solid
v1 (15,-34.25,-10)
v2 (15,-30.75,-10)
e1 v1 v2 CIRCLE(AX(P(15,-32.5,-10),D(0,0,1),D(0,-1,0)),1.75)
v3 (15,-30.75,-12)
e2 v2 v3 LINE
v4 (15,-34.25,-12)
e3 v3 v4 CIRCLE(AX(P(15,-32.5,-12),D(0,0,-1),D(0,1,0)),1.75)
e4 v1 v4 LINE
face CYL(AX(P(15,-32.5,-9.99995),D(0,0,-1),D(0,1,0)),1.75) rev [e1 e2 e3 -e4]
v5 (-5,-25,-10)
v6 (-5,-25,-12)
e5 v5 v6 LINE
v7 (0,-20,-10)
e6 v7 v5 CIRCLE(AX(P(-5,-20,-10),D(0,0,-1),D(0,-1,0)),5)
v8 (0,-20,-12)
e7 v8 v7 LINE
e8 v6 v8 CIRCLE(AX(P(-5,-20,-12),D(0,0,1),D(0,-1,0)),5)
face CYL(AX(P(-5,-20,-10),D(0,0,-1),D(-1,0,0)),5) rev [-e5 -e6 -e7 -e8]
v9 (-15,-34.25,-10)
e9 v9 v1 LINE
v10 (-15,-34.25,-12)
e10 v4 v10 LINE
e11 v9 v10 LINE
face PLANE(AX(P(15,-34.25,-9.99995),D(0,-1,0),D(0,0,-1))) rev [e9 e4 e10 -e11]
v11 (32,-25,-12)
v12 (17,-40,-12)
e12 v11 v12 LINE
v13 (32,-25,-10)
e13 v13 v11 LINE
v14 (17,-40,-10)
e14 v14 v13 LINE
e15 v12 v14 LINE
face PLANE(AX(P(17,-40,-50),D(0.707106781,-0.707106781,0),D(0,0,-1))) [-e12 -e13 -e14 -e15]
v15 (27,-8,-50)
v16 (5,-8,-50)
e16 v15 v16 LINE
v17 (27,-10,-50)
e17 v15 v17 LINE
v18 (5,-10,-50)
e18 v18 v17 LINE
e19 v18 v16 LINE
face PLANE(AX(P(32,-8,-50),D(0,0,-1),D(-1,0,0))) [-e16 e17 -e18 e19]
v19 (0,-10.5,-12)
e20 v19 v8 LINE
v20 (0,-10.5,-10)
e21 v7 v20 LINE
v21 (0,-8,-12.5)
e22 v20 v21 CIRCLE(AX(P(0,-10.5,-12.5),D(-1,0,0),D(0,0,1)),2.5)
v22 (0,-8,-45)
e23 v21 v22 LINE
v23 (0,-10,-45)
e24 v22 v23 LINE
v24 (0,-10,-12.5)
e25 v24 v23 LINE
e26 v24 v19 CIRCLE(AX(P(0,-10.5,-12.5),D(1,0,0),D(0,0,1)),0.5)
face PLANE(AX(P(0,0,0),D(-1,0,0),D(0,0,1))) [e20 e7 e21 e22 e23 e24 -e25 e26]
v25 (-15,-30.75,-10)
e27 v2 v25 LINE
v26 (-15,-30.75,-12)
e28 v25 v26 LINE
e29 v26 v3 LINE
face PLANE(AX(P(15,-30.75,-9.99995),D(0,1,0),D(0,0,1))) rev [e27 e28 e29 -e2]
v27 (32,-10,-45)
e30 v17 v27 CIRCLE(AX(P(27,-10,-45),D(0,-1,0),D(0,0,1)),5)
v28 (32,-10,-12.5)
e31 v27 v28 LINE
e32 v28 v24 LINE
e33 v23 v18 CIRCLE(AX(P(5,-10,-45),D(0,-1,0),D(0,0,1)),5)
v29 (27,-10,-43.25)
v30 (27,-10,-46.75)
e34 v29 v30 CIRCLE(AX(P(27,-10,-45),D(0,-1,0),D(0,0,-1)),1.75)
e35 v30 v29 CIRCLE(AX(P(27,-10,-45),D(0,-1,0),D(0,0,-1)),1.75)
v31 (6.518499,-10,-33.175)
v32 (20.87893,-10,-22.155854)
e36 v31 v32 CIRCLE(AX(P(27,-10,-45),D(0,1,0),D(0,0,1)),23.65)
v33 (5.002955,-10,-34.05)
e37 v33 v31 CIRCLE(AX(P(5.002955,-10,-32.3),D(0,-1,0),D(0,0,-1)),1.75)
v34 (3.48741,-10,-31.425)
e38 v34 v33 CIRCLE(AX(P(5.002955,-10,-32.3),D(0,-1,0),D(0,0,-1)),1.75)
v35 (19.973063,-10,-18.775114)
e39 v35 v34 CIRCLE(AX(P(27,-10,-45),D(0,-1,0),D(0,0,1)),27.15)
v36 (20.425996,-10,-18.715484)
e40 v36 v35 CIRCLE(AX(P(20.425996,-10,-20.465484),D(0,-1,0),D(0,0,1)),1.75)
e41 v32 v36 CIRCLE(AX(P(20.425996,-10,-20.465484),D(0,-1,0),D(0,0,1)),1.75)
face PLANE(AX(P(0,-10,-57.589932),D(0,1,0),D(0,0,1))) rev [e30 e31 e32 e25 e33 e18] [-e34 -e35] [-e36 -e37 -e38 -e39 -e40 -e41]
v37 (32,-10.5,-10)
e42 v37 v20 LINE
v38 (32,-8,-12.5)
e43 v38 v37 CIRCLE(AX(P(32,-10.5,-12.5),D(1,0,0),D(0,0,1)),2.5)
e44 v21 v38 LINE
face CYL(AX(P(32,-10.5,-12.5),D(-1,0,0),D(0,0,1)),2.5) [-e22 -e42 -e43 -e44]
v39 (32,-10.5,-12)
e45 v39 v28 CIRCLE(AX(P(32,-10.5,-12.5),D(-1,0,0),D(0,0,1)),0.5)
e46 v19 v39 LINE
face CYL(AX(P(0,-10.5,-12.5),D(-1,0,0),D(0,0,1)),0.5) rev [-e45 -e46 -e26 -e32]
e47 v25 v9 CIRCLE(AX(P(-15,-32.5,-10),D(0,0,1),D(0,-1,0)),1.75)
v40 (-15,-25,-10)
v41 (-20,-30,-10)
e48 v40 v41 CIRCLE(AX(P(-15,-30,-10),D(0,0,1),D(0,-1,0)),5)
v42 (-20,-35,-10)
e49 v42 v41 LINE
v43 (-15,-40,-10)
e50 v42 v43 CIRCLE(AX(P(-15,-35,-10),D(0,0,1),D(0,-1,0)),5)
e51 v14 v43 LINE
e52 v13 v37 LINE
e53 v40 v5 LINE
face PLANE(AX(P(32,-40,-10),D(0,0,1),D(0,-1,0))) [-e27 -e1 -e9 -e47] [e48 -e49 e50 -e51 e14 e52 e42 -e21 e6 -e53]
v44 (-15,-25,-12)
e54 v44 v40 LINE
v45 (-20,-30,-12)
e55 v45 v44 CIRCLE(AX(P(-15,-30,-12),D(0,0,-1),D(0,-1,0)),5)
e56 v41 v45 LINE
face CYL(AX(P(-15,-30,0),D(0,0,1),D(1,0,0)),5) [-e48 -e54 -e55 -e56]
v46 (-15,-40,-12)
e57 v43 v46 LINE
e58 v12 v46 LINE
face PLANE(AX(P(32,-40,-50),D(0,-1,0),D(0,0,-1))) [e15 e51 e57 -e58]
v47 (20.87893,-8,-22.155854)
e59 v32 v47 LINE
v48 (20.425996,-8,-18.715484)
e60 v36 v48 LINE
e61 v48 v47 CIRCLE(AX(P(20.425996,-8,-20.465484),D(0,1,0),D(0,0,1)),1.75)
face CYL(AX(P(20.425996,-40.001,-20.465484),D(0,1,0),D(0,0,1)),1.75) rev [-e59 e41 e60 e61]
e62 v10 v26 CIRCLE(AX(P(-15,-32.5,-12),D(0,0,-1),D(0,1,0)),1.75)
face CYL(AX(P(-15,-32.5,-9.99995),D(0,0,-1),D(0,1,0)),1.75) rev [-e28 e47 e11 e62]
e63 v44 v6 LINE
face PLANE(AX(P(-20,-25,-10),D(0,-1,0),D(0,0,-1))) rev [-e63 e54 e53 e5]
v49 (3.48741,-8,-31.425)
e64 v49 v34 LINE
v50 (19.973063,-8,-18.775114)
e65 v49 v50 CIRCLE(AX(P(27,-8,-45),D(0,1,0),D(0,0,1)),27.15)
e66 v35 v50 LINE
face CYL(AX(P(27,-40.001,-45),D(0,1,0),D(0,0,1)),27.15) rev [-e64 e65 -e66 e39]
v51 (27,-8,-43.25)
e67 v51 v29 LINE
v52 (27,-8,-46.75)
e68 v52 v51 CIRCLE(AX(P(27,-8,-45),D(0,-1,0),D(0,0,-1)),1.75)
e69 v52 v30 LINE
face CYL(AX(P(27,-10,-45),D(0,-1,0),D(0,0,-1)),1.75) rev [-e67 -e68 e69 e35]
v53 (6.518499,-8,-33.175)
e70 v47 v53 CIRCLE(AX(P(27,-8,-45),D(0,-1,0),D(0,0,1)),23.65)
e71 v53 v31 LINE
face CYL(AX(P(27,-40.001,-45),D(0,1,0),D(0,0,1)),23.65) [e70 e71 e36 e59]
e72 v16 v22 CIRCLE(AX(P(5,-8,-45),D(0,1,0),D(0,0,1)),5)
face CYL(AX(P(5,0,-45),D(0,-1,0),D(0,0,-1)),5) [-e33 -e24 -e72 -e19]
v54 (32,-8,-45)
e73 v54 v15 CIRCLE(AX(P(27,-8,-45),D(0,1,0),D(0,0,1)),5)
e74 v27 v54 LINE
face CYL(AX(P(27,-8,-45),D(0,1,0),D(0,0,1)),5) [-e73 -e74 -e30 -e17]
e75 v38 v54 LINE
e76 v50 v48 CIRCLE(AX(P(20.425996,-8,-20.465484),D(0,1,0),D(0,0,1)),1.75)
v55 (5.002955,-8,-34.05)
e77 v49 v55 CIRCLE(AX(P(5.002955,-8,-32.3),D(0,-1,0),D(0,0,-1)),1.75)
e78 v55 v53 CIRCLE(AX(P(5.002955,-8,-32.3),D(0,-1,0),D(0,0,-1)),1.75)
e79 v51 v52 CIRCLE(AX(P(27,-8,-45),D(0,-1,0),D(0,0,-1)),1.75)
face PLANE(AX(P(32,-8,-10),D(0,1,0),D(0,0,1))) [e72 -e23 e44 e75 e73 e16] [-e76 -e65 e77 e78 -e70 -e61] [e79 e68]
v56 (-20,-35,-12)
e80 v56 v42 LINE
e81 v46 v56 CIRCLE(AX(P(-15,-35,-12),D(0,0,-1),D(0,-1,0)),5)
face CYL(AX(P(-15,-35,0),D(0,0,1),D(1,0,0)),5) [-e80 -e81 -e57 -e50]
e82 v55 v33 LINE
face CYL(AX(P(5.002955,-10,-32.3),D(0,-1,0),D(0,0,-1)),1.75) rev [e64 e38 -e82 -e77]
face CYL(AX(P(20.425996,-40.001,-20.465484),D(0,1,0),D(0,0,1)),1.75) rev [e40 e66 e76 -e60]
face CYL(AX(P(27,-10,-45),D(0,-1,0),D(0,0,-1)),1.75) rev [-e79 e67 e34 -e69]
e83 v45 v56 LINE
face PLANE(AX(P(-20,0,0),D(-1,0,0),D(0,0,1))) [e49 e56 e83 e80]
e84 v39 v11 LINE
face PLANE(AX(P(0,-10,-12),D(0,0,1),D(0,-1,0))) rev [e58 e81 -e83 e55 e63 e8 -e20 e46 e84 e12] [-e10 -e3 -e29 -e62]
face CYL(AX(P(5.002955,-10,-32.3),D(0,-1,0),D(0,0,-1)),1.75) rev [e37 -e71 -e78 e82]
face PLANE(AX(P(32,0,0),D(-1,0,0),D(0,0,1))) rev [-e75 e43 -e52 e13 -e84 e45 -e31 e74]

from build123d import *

# Parameters (mm, degrees)
SKETCH_1_W              = 32
SKETCH_1_H              = 40
EXTRUDE_1_DEPTH         = 32
SKETCH_2_W              = 45.589932218
SKETCH_2_H              = 35.821991612
CUT_EXTRUDE_1_DEPTH     = 72.582120673
HOLE_WIZARD_3_5_3_5_1_D = 3.5
FILLET_1_R              = 0.5
FILLET_3_R              = 2.5
CUT_EXTRUDE_3_REACH     = 69.439
SKETCH_9_W              = 2
SKETCH_9_H              = 15
EXTRUDE_2_DEPTH         = 20
CUT_EXTRUDE_4_DEPTH     = 64.780874876
CHAMFER_1_SIZE          = 15
FILLET_4_R              = 5


with BuildPart() as part:
    # 草图1 → 凸台-拉伸1 (new body)
    with BuildSketch(Plane(origin=(0, 0, 0), x_dir=(0, -1, 0), z_dir=(-1, 0, 0))):
        with Locations((24, -30)):
            Rectangle(SKETCH_1_W, SKETCH_1_H)
    extrude(amount=-EXTRUDE_1_DEPTH)

    # 草图2 → 切除-拉伸1 (cut, through all)
    with BuildSketch(Plane(origin=(32, 0, 0), x_dir=(0, 0, -1), z_dir=(1, 0, 0))):
        with Locations((34.794966109, -27.910995806)):
            Rectangle(SKETCH_2_W, SKETCH_2_H)
    extrude(amount=-CUT_EXTRUDE_1_DEPTH, mode=Mode.SUBTRACT)

    # Ø3.5 (3.5) 直径孔1 (through all)
    with Locations(Plane(origin=(0, -10, 0), x_dir=(-1, 0, 0), z_dir=(0, -1, 0))):
        with Locations((-5.002954744, 32.3), (-27, 45)):
            Hole(HOLE_WIZARD_3_5_3_5_1_D / 2)

    # 圆角1
    fillet_1_edges = [part.edges().sort_by_distance(p)[0] for p in [
        (16, -10, -12),
    ]]
    fillet(fillet_1_edges, radius=FILLET_1_R)

    # 圆角3
    fillet_3_edges = [part.edges().sort_by_distance(p)[0] for p in [
        (16, -8, -10),
    ]]
    fillet(fillet_3_edges, radius=FILLET_3_R)

    # 草图8 → 切除-拉伸3 (cut, up to next)
    with BuildSketch(Plane(origin=(0, -8, 0), x_dir=(1, 0, 0), z_dir=(0, 1, 0)), mode=Mode.PRIVATE) as cut_extrude_3_sk1:
        with BuildLine():
            ThreePointArc((3.487410287, 31.425), (10.472127202, 23.460456811), (19.973062925, 18.775113816))
            ThreePointArc((19.973062925, 18.775113816), (22.11636645, 20.012550683), (20.878929583, 22.155854208))
            ThreePointArc((20.878929583, 22.155854208), (12.602792204, 26.237193502), (6.5184992, 33.175))
            ThreePointArc((6.5184992, 33.175), (4.127954744, 33.815544457), (3.487410287, 31.425))
        make_face()
    cut_extrude_3_tool1 = extrude(cut_extrude_3_sk1.sketch, amount=-CUT_EXTRUDE_3_REACH, mode=Mode.PRIVATE) & part.part
    add(cut_extrude_3_tool1.solids().sort_by_distance((12.026611, -8, -25.486299))[0], mode=Mode.SUBTRACT)

    # 草图9 → 凸台-拉伸2 (add)
    with BuildSketch(Plane.ZY):
        with Locations((-11, -32.5)):
            Rectangle(SKETCH_9_W, SKETCH_9_H)
    extrude(amount=EXTRUDE_2_DEPTH)

    # 草图10 → 切除-拉伸4 (cut, through all)
    with BuildSketch(Plane(origin=(0, 0, -12), x_dir=(-1, 0, 0), z_dir=(0, 0, -1))):
        with BuildLine():
            Line((-15, -30.75), (15, -30.75))
            ThreePointArc((15, -30.75), (16.75, -32.5), (15, -34.25))
            Line((15, -34.25), (-15, -34.25))
            ThreePointArc((-15, -34.25), (-16.75, -32.5), (-15, -30.75))
        make_face()
    extrude(amount=-CUT_EXTRUDE_4_DEPTH, mode=Mode.SUBTRACT)

    # 倒角1
    chamfer_1_edges = [part.edges().sort_by_distance(p)[0] for p in [
        (32, -40, -11),
    ]]
    chamfer(chamfer_1_edges, length=CHAMFER_1_SIZE)

    # 圆角4
    fillet_4_edges = [part.edges().sort_by_distance(p)[0] for p in [
        (-20, -40, -11),
        (0, -25, -11),
        (-20, -25, -11),
        (0, -9, -50),
        (32, -9, -50),
    ]]
    fillet(fillet_4_edges, radius=FILLET_4_R)


solid = part.part
